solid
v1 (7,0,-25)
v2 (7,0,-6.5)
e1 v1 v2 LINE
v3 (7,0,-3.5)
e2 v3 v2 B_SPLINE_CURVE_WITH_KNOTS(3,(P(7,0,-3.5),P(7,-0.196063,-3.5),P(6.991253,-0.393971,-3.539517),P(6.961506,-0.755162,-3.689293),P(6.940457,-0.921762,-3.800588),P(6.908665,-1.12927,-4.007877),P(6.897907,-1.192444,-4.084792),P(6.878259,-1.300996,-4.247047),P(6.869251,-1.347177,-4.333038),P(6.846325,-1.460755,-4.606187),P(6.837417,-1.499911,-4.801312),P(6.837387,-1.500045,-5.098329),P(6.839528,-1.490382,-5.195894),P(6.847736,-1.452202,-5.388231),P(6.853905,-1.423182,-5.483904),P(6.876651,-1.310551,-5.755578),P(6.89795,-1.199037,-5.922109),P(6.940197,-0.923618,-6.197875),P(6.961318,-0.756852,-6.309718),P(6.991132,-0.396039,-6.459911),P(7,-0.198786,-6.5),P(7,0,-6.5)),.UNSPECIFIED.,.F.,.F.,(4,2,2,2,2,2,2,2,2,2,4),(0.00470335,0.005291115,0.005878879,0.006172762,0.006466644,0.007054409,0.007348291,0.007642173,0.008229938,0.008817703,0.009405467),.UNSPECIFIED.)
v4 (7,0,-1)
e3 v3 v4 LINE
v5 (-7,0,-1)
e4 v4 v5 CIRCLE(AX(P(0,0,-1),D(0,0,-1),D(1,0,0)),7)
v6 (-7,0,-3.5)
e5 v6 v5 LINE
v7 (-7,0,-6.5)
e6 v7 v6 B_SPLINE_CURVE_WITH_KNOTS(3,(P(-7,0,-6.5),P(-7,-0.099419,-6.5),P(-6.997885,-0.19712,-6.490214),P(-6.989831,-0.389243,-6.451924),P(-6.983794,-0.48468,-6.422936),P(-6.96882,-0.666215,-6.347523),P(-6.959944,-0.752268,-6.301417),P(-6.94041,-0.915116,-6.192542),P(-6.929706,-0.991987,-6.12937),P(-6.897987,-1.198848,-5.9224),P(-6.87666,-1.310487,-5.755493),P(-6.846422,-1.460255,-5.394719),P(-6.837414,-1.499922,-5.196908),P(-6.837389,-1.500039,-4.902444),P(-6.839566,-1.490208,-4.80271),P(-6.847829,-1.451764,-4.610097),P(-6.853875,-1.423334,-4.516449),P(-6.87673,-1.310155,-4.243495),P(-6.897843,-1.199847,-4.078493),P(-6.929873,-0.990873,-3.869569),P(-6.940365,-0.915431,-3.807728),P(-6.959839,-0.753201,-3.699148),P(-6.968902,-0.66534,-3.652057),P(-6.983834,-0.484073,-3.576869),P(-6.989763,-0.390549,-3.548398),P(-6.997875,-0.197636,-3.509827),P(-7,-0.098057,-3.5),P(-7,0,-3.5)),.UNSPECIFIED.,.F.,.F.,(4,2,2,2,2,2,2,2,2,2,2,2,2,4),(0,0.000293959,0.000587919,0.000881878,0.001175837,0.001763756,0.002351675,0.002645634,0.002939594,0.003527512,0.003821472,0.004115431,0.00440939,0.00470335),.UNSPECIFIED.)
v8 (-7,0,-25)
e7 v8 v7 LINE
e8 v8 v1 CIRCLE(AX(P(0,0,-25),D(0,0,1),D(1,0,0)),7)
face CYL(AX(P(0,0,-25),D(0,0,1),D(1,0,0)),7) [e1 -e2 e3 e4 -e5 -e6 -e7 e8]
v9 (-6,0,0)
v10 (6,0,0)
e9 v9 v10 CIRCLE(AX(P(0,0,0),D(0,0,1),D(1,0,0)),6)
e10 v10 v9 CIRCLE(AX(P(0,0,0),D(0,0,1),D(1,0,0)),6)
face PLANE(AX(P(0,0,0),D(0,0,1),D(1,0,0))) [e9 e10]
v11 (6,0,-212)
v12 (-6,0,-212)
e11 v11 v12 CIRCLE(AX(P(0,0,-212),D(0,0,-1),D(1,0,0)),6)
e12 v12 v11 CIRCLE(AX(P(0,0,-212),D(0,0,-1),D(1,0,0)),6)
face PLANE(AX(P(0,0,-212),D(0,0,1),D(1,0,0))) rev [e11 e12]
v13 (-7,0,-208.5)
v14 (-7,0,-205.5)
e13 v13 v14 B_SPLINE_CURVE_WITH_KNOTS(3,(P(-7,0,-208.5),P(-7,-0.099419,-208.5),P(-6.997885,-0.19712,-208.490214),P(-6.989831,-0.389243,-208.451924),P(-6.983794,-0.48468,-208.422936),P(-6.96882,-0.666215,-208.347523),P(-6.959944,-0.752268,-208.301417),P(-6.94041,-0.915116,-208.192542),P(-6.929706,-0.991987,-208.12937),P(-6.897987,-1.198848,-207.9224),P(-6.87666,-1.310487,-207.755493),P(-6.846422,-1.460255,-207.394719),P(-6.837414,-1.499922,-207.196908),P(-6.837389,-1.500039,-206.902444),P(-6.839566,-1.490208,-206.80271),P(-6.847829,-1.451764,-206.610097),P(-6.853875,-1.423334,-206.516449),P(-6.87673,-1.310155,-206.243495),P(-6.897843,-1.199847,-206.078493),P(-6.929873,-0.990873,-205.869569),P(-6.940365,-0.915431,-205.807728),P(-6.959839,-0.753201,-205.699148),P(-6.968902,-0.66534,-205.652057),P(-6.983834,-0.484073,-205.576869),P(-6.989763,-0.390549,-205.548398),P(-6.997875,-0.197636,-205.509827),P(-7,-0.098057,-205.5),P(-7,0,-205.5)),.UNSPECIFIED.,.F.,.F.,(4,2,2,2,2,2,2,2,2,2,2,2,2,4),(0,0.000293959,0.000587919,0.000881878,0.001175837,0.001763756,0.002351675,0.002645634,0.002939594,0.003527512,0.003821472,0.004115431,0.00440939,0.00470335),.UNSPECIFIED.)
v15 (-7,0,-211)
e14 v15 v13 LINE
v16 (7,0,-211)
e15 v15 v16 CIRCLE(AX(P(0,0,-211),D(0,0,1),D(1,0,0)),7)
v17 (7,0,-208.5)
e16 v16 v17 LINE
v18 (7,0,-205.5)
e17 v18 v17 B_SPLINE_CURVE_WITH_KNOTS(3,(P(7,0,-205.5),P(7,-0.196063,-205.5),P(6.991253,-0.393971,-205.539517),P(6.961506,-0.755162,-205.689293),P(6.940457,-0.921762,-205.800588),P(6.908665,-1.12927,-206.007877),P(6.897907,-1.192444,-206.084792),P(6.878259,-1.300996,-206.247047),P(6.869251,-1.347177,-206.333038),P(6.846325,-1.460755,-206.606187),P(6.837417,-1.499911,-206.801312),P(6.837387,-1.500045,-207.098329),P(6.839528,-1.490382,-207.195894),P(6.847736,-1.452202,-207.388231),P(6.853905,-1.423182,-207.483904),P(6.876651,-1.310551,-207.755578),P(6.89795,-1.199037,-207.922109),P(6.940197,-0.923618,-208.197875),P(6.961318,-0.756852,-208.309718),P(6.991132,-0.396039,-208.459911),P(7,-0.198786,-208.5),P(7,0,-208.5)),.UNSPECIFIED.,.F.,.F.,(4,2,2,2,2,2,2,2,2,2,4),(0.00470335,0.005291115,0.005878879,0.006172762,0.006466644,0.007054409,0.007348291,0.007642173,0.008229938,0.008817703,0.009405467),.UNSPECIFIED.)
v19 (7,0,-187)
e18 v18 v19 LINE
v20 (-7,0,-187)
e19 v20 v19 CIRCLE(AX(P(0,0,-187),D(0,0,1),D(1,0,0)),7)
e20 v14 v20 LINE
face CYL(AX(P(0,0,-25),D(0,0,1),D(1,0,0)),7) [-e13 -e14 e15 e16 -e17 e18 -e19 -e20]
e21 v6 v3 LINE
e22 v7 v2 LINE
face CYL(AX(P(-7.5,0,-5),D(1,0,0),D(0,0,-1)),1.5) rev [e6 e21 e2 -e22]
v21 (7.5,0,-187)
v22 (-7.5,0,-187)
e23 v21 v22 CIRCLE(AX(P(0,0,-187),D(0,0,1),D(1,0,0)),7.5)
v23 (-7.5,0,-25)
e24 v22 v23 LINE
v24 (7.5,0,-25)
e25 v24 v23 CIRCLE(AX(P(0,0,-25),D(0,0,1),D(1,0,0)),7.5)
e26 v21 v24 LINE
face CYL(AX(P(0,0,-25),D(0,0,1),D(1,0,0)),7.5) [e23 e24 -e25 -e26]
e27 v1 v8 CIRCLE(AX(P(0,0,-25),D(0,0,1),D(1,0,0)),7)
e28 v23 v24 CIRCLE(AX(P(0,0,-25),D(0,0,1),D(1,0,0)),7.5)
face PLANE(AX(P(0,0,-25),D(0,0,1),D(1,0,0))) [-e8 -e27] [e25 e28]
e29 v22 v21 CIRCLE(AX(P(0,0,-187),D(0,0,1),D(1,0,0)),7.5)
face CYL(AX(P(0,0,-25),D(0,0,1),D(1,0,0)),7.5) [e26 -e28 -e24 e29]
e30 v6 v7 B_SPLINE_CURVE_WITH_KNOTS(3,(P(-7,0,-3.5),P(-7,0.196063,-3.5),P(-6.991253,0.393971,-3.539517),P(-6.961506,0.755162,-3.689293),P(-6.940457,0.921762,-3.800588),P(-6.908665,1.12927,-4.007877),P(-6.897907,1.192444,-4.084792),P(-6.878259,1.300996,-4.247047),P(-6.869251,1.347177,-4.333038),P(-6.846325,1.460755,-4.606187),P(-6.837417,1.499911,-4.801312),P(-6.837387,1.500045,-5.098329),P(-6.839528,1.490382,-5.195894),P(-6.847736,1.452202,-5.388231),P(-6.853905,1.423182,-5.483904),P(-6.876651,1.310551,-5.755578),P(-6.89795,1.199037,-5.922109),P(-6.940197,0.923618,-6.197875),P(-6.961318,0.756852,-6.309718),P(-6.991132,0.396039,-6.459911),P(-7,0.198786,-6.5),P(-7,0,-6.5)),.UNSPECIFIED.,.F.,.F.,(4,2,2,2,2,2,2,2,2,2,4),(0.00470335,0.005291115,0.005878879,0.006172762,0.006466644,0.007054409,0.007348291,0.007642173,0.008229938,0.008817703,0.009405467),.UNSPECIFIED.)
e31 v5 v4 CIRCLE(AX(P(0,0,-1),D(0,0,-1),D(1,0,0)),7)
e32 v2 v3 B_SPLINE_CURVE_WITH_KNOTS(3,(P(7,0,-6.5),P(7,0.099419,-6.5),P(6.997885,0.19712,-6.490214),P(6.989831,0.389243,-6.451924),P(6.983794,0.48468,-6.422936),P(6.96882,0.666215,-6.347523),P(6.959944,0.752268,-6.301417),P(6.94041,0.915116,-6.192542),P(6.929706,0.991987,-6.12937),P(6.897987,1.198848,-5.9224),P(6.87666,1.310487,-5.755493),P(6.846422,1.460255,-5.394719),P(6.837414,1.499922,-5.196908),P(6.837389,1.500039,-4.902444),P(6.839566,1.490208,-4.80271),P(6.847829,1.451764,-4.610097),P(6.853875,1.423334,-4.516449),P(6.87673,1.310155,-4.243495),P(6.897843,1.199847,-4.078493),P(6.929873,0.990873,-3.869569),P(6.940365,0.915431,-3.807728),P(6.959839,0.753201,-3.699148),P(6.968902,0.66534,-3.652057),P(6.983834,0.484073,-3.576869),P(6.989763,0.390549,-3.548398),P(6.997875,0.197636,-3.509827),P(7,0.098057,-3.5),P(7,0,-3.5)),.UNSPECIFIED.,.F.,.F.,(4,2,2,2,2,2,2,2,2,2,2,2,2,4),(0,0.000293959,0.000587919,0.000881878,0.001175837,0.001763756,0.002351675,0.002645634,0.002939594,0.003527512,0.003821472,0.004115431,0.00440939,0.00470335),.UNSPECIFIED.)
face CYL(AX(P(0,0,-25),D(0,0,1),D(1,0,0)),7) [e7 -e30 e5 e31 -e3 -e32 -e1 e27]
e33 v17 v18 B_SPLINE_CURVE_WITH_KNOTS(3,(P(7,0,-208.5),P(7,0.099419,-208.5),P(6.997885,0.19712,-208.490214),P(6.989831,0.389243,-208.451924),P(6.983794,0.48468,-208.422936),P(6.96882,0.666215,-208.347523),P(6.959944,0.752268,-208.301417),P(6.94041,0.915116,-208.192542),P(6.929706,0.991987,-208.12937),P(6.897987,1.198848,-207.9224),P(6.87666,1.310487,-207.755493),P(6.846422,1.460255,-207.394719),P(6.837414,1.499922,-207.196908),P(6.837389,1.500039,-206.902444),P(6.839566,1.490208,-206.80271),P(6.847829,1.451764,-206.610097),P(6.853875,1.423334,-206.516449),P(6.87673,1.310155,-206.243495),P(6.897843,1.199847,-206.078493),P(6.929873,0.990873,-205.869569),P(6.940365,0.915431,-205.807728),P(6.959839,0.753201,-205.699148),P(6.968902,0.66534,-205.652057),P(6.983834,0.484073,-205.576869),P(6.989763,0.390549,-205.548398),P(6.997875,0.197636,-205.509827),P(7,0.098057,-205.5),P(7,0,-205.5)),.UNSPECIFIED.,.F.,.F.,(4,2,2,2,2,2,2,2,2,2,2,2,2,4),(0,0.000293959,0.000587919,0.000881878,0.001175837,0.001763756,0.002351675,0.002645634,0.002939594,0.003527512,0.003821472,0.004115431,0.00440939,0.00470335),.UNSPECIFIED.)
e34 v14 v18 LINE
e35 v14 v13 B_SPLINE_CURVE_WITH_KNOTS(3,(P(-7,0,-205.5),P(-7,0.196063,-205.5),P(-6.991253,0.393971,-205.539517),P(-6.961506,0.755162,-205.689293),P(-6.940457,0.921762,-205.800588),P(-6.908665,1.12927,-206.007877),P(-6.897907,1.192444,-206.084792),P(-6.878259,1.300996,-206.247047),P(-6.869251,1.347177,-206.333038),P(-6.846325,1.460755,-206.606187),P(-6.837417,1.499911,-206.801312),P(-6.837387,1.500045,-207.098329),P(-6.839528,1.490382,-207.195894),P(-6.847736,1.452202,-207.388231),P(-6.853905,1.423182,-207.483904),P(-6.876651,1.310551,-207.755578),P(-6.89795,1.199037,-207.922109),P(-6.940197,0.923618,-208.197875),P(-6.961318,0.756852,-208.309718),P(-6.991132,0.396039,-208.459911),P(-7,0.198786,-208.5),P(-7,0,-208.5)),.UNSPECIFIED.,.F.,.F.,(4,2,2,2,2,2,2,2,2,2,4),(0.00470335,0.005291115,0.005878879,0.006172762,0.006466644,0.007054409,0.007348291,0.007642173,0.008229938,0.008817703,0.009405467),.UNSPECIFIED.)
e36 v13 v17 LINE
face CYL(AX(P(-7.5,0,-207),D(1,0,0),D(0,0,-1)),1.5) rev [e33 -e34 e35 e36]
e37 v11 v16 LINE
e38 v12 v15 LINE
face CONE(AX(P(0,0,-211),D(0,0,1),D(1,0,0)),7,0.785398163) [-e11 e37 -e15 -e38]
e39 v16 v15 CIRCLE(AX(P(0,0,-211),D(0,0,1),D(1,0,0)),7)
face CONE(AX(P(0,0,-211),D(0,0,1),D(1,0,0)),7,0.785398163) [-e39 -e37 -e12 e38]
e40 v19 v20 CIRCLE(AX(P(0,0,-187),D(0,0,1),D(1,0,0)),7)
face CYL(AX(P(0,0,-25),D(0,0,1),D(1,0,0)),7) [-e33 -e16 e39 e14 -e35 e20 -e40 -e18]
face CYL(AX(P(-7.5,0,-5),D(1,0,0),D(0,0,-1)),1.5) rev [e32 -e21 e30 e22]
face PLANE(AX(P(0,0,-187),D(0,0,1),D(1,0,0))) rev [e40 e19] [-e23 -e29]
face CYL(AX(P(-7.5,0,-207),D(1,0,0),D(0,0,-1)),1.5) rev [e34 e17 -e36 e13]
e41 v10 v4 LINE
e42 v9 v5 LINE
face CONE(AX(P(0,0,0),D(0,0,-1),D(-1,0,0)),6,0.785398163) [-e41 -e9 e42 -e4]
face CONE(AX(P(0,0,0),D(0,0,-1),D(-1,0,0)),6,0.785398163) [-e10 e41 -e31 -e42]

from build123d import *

# Parameters (mm, degrees)
SKETCH1_W               = 25
SKETCH1_H               = 7
CUT_EXTRUDE1_DEPTH      = 213.265164358
CUT_EXTRUDE1_DEPTH_BACK = 213.265164358
SKETCH2_R               = 1.5
CHAMFER1_SIZE           = 1


with BuildPart() as part:
    # Sketch1 → Revolve1 (revolve)
    with BuildSketch(Plane(origin=(0, 0, 0), x_dir=(0, 0, -1), z_dir=(1, 0, 0)), mode=Mode.PRIVATE) as revolve1_sk:
        with Locations((12.5, 3.5)):
            Rectangle(SKETCH1_W, SKETCH1_H)
        Polygon((25, 7), (25, 0), (187, 0), (187, 7), (187, 7.5), (25, 7.5), align=None)
        with Locations((199.5, 3.5)):
            Rectangle(SKETCH1_W, SKETCH1_H)
    revolve(revolve1_sk.sketch.rotate(Axis((0, 0, -25), (0, 0, -1)), 90), axis=Axis((0, 0, -25), (0, 0, -1)))

    # Sketch2 → Cut-Extrude1 (cut, two sides: drawn at the far end of the back side and taken through both)
    with BuildSketch(Plane(origin=(0, 0, 0), x_dir=(0, 0, -1), z_dir=(1, 0, 0)).offset(-CUT_EXTRUDE1_DEPTH_BACK)):
        with Locations((5, 0)):
            Circle(SKETCH2_R)
        with Locations((207, 0)):
            Circle(SKETCH2_R)
    extrude(amount=CUT_EXTRUDE1_DEPTH + CUT_EXTRUDE1_DEPTH_BACK, mode=Mode.SUBTRACT)

    # Chamfer1
    chamfer1_edges = [part.edges().sort_by_distance(p)[0] for p in [
        (-7, 0, 0),
        (-7, 0, -212),
    ]]
    chamfer(chamfer1_edges, length=CHAMFER1_SIZE)


solid = part.part
